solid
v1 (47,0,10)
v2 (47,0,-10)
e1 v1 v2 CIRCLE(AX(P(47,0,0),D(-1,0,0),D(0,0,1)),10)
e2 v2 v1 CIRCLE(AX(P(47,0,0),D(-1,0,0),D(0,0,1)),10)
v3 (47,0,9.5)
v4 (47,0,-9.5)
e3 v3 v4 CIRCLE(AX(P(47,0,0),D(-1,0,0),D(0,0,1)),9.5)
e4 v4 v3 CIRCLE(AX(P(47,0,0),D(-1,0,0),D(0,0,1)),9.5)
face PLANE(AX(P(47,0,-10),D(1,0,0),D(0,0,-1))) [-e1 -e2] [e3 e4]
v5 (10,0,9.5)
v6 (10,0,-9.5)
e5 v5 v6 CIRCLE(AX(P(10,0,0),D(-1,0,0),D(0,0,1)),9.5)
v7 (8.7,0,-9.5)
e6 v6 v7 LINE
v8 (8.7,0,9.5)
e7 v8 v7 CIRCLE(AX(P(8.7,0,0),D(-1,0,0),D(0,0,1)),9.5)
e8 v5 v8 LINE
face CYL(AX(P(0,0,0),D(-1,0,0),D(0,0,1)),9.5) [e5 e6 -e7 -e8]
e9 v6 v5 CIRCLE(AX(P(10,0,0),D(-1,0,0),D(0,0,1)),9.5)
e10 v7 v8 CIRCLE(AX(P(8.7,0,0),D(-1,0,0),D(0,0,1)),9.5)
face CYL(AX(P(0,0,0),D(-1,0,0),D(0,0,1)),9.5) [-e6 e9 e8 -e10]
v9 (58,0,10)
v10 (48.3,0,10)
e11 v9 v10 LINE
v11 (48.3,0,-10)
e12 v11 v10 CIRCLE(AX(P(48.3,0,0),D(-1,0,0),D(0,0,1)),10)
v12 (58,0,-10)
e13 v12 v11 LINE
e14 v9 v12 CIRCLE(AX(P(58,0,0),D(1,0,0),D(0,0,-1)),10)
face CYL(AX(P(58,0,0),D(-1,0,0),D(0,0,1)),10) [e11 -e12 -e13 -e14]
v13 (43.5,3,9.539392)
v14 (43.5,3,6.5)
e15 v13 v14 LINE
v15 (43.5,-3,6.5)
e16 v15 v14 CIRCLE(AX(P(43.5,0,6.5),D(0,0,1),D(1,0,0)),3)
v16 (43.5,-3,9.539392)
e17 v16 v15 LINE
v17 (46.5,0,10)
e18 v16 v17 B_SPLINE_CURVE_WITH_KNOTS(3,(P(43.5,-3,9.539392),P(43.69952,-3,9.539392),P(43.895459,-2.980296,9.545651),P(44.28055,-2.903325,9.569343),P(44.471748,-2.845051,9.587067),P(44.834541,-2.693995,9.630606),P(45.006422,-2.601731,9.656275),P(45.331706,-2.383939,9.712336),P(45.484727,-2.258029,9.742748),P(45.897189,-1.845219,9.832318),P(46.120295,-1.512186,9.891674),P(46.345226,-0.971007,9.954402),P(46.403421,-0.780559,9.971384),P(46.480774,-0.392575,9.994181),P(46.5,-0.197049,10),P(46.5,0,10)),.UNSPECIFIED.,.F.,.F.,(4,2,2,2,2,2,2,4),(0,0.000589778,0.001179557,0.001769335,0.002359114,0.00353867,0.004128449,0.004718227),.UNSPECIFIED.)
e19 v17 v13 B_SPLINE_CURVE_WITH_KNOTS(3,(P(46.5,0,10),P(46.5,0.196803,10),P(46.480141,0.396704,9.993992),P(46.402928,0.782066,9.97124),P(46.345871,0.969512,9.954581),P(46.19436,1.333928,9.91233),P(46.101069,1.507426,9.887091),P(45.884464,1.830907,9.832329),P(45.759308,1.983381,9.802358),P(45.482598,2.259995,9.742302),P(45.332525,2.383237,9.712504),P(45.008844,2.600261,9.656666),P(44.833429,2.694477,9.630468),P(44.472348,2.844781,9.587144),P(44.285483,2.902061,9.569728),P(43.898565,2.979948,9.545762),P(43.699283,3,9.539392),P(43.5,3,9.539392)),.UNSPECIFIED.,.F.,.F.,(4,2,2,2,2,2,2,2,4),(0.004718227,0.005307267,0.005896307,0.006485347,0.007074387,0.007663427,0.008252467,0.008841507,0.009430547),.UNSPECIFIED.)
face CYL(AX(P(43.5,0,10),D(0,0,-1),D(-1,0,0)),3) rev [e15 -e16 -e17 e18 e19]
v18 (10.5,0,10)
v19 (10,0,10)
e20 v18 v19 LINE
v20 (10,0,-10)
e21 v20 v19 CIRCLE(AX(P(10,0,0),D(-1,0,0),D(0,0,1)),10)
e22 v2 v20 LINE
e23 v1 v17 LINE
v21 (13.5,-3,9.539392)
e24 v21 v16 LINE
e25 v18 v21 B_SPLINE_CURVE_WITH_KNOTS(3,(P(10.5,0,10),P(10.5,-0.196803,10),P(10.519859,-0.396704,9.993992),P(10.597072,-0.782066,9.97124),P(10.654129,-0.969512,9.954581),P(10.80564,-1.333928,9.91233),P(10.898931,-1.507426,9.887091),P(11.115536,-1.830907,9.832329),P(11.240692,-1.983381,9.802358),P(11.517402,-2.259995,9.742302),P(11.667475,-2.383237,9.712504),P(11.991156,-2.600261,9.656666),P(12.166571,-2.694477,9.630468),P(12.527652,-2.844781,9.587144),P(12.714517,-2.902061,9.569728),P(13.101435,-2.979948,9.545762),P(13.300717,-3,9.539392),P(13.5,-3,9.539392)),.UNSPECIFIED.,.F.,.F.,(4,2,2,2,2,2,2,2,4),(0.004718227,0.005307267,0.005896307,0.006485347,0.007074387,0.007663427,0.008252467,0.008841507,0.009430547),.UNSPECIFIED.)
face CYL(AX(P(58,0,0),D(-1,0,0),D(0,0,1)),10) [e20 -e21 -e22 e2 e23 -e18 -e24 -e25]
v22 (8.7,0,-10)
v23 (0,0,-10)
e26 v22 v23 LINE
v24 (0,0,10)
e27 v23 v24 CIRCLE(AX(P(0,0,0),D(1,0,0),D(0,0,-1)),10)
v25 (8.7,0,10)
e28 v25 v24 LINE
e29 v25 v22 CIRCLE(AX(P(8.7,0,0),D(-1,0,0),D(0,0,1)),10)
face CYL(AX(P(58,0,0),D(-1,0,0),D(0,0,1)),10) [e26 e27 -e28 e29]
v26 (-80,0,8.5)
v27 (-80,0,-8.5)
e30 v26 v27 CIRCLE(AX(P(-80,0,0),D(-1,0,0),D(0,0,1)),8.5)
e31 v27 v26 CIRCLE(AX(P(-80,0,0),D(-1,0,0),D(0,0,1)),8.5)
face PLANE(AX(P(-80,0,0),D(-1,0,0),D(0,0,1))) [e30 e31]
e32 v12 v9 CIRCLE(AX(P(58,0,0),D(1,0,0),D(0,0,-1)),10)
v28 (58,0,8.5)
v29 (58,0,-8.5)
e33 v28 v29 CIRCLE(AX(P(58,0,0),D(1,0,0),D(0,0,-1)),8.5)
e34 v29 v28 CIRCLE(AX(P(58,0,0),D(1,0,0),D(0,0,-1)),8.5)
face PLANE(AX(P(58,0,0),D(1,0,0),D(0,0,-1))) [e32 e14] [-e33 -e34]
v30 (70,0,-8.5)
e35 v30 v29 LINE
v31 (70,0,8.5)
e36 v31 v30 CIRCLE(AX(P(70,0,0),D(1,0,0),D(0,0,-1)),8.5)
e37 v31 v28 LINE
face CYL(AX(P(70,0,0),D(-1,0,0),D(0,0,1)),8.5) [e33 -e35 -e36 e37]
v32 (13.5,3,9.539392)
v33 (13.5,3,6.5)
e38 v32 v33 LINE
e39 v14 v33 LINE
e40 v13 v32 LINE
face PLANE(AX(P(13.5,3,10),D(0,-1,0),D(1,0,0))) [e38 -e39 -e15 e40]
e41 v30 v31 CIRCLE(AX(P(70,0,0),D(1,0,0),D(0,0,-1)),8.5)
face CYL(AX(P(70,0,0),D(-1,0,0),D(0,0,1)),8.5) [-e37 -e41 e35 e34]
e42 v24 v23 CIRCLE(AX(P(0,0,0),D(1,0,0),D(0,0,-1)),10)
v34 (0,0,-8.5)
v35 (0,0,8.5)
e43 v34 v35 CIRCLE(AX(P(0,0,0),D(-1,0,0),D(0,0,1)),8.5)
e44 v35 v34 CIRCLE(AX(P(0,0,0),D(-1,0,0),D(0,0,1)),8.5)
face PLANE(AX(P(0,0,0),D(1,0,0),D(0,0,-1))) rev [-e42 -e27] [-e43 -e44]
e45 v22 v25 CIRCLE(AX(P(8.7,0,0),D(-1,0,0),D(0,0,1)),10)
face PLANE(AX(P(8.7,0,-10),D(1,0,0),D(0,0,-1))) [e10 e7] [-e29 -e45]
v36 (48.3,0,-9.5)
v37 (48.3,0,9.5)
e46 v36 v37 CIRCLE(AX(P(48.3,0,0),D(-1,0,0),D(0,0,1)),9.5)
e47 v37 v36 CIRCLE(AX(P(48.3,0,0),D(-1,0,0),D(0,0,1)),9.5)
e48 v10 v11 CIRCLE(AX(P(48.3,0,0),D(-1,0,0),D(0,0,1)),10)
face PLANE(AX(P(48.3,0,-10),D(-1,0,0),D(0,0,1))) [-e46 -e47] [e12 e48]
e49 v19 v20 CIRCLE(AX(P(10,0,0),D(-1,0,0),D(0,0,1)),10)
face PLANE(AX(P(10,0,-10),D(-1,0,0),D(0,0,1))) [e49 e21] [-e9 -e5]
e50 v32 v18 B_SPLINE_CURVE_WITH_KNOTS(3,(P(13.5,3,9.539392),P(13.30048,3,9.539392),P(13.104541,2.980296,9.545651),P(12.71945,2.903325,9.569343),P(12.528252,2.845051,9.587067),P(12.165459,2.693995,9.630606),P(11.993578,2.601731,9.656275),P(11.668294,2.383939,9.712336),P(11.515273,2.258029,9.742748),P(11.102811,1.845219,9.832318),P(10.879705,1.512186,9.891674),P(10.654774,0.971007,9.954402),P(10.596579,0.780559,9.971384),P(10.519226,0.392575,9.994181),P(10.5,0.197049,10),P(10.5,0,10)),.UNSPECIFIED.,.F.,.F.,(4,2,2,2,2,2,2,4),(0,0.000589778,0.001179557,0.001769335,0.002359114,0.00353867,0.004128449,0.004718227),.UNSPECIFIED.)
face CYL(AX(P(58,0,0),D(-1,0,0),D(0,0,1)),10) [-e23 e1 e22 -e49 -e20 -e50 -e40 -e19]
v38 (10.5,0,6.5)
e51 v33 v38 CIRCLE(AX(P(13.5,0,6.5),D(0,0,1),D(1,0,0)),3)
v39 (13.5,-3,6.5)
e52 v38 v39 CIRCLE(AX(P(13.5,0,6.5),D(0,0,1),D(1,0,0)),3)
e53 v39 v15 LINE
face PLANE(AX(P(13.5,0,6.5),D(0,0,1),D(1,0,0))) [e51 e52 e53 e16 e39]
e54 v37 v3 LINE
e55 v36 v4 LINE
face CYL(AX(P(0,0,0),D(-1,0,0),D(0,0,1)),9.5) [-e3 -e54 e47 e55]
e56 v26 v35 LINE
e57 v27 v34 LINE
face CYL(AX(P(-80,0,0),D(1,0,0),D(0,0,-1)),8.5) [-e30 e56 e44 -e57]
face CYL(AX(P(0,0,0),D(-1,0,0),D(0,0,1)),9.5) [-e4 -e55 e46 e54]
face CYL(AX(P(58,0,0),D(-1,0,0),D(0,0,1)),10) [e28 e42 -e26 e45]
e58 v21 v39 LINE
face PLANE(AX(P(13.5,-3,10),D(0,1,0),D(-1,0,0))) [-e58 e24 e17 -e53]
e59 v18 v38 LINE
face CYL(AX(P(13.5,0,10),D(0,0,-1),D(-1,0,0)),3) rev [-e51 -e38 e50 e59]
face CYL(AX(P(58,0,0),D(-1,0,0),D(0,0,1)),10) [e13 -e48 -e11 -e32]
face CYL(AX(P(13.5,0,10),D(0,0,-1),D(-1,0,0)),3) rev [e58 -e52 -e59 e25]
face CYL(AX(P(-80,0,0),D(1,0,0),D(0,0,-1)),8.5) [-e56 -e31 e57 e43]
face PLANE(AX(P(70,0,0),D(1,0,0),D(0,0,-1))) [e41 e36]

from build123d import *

# Parameters (mm, degrees)
SKETCH_1_R          = 10
EXTRUDE_1_DEPTH     = 58
SKETCH_2_R          = 8.5
EXTRUDE_2_DEPTH     = 12
EXTRUDE_START       = 80
SKETCH_3_R          = 8.5
EXTRUDE_3_DEPTH     = 80
CUT_EXTRUDE_1_DEPTH = 83.29368141
SKETCH_5_W          = 1.3
SKETCH_5_H          = 0.5


with BuildPart() as part:
    # 草图1 → 凸台-拉伸1 (new body)
    with BuildSketch(Plane(origin=(0, 0, 0), x_dir=(0, 0, -1), z_dir=(1, 0, 0))):
        with Locations(Location((0, 0, 0), (0, 0, 180))):
            Circle(SKETCH_1_R)
    extrude(amount=EXTRUDE_1_DEPTH)

    # 草图2 → 凸台-拉伸2 (add)
    with BuildSketch(Plane(origin=(58, 0, 0), x_dir=(0, 0, -1), z_dir=(1, 0, 0))):
        Circle(SKETCH_2_R)
    extrude(amount=EXTRUDE_2_DEPTH)

    # 草图3 → 凸台-拉伸3 (add)
    with BuildSketch(Plane.ZY.offset(EXTRUDE_START)):
        with Locations(Location((0, 0, 0), (0, 0, 180))):
            Circle(SKETCH_3_R)
    extrude(amount=-EXTRUDE_3_DEPTH)

    # 草图4 → 切除-拉伸1 (cut, through all)
    with BuildSketch(Plane.XY.offset(6.5)):
        with BuildLine():
            Line((13.5, 3), (43.5, 3))
            ThreePointArc((43.5, 3), (46.5, 0), (43.5, -3))
            Line((43.5, -3), (13.5, -3))
            ThreePointArc((13.5, -3), (10.5, 0), (13.5, 3))
        make_face()
    extrude(amount=CUT_EXTRUDE_1_DEPTH, mode=Mode.SUBTRACT)

    # 草图5 → 切除-旋转1 (revolve, cut)
    with BuildSketch(Plane(origin=(0, 0, 0), x_dir=(1, 0, 0), z_dir=(0, 1, 0)), mode=Mode.PRIVATE) as cut_revolve_1_sk:
        with Locations((9.35, 9.75)):
            Rectangle(SKETCH_5_W, SKETCH_5_H)
        with Locations((47.65, 9.75)):
            Rectangle(SKETCH_5_W, SKETCH_5_H)
    revolve(cut_revolve_1_sk.sketch.rotate(Axis((0, 0, 0), (1, 0, 0)), 180), axis=Axis((0, 0, 0), (1, 0, 0)), mode=Mode.SUBTRACT)


solid = part.part
